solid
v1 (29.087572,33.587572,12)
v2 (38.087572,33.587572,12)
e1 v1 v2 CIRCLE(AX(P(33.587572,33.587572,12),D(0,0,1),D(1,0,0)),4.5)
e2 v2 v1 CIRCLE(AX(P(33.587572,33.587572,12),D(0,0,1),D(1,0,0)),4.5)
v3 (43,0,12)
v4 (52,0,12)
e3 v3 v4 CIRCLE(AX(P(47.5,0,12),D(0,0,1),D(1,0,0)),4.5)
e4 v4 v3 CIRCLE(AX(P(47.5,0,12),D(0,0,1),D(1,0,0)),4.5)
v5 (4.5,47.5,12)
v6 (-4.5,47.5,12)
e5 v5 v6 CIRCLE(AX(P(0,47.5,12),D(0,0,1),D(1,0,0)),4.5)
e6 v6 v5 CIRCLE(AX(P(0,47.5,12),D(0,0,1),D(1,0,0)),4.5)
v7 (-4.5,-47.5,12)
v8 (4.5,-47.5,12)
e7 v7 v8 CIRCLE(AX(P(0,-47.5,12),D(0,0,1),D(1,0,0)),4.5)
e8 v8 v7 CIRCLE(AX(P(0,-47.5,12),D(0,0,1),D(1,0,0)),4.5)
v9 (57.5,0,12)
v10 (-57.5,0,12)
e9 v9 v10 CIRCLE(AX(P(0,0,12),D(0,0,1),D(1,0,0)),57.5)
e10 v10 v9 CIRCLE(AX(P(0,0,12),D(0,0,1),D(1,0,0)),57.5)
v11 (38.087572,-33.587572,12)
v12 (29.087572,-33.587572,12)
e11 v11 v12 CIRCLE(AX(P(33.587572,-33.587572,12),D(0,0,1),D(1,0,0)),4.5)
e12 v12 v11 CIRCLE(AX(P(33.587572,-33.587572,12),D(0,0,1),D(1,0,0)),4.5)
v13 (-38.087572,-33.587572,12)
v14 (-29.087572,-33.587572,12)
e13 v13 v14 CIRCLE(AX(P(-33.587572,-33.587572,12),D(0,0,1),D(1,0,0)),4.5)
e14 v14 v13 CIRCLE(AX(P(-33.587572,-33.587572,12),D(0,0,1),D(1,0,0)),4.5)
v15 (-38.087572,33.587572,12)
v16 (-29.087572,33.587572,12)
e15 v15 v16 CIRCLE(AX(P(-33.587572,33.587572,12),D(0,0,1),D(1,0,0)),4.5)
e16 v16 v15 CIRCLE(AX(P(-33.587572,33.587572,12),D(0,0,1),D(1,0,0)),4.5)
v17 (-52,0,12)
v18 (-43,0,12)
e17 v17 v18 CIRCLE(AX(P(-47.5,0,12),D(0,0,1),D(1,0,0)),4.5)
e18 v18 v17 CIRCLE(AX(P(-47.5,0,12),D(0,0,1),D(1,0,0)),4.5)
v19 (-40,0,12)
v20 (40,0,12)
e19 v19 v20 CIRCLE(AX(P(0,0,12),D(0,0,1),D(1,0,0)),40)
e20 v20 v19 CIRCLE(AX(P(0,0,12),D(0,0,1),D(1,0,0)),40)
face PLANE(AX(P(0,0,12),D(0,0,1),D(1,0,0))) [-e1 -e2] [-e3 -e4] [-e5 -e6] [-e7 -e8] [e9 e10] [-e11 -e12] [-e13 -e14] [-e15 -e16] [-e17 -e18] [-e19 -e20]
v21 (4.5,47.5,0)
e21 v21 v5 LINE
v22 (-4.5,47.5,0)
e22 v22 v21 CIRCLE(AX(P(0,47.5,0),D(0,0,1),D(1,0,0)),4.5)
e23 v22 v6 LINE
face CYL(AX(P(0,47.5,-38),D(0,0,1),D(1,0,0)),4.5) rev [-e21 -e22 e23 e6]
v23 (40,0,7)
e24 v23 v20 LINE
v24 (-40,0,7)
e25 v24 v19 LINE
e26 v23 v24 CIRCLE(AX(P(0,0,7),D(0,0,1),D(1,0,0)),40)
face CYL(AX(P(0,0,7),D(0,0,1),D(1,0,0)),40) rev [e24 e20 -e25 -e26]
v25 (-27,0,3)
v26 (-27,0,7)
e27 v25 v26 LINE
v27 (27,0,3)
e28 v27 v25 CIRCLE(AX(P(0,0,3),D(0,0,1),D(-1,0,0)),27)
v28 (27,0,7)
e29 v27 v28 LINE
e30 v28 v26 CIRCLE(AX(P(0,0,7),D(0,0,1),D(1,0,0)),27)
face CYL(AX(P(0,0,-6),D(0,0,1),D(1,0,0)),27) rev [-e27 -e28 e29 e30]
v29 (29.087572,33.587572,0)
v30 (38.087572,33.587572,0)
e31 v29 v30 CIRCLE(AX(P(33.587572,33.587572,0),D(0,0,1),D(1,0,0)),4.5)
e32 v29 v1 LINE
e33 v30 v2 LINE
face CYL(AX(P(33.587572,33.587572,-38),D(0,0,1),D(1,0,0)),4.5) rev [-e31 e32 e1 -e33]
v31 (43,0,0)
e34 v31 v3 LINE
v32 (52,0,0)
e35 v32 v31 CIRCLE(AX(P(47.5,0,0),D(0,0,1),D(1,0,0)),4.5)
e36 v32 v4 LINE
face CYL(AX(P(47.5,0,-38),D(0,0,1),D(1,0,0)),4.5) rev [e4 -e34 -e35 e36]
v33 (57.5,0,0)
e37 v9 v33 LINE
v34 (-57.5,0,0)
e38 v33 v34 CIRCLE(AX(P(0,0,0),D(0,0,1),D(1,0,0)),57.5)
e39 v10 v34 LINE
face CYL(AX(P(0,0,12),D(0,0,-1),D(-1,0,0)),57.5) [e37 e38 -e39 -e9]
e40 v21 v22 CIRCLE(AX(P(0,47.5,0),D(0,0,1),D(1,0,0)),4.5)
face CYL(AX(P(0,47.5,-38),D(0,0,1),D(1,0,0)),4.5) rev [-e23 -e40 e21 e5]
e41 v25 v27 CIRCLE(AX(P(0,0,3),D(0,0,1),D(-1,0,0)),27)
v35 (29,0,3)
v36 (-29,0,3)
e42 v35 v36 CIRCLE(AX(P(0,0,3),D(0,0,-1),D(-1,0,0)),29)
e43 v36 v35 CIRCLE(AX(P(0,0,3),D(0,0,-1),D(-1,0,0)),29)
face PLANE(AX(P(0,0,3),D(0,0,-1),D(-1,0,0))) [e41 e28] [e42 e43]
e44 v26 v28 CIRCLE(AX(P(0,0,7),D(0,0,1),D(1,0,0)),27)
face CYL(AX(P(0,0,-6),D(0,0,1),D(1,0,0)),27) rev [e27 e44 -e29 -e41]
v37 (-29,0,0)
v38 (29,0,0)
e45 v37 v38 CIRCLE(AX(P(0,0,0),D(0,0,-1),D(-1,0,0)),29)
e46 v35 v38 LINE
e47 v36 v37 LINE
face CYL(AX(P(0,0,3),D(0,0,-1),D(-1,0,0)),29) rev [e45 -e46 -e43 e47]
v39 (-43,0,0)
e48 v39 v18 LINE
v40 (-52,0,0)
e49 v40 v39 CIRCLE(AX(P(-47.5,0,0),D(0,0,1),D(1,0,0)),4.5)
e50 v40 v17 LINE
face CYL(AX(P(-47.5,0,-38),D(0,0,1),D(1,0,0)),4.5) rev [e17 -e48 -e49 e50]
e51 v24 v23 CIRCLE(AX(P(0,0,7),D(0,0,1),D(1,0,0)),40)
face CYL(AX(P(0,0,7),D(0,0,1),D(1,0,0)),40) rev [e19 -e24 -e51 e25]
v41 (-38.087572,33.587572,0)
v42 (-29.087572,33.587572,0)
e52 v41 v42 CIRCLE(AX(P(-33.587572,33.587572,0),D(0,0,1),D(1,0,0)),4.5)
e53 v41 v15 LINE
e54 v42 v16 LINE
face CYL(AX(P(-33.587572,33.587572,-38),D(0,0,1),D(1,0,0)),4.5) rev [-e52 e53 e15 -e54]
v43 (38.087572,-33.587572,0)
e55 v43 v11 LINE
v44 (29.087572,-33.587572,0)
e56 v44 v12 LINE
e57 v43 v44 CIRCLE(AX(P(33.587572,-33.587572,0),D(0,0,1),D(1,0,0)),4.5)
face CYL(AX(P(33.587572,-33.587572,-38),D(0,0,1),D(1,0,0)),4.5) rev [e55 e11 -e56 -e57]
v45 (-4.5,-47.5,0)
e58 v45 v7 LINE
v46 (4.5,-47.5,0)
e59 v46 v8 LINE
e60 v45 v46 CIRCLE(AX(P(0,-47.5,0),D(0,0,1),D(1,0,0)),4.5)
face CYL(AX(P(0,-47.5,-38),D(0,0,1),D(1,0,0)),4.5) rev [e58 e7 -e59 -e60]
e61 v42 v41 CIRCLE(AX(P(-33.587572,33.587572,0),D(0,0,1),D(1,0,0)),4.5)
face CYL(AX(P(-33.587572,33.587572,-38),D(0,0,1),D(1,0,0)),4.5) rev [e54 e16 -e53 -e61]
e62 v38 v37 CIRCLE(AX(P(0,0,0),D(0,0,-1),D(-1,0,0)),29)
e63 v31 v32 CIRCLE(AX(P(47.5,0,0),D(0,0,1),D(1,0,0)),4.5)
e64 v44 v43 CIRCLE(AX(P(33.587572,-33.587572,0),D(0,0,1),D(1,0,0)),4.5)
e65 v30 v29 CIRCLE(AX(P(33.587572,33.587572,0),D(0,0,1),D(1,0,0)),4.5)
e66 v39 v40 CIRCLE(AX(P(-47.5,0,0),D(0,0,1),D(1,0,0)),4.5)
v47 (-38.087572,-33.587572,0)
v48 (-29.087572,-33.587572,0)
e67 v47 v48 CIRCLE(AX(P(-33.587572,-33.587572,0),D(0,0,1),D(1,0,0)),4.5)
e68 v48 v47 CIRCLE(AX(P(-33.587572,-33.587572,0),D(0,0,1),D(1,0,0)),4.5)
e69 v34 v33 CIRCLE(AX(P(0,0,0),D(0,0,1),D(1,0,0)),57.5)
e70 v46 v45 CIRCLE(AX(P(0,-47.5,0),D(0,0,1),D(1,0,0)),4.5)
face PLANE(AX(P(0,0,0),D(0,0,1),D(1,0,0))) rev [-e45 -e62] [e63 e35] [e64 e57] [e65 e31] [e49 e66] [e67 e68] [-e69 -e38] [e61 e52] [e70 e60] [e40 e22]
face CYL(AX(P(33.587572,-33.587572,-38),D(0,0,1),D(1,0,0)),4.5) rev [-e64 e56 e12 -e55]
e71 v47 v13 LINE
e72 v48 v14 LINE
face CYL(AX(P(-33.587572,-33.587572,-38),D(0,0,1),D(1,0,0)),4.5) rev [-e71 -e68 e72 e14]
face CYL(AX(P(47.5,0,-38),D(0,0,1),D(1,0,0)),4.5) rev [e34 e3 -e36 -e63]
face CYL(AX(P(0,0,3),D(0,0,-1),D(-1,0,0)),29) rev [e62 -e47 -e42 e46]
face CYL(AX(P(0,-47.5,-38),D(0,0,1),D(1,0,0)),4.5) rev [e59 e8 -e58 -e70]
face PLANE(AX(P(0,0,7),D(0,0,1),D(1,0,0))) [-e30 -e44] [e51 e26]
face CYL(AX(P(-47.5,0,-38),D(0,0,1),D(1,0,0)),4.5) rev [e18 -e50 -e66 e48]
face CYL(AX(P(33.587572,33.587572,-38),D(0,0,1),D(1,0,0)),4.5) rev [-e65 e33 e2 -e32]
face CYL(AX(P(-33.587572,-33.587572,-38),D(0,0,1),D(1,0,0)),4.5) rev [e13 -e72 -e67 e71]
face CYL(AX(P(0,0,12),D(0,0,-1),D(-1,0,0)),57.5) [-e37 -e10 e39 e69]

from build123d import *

# Parameters (mm, degrees)
SKETCH_1_R          = 57.5
EXTRUDE_1_DEPTH     = 12
SKETCH_2_R          = 40
CUT_EXTRUDE_1_DEPTH = 5
SKETCH_3_R          = 27
CUT_EXTRUDE_2_DEPTH = 13
SKETCH_4_R          = 29
CUT_EXTRUDE_3_DEPTH = 3
SKETCH_5_R          = 4.5
CUT_EXTRUDE_4_DEPTH = 50


with BuildPart() as part:
    # 草图1 → 凸台-拉伸1 (new body)
    with BuildSketch(Plane.XY):
        Circle(SKETCH_1_R)
    extrude(amount=EXTRUDE_1_DEPTH)

    # 草图2 → 切除-拉伸1 (cut)
    with BuildSketch(Plane.XY.offset(12)):
        Circle(SKETCH_2_R)
    extrude(amount=-CUT_EXTRUDE_1_DEPTH, mode=Mode.SUBTRACT)

    # 草图3 → 切除-拉伸2 (cut)
    with BuildSketch(Plane.XY.offset(7)):
        Circle(SKETCH_3_R)
    extrude(amount=-CUT_EXTRUDE_2_DEPTH, mode=Mode.SUBTRACT)

    # 草图4 → 切除-拉伸3 (cut)
    with BuildSketch(Plane(origin=(0, 0, 0), x_dir=(-1, 0, 0), z_dir=(0, 0, -1))):
        Circle(SKETCH_4_R)
    extrude(amount=-CUT_EXTRUDE_3_DEPTH, mode=Mode.SUBTRACT)

    # 草图5 → 切除-拉伸4 (cut)
    with BuildSketch(Plane.XY.offset(12)):
        with Locations((0, 47.5)):
            Circle(SKETCH_5_R)
        with Locations((33.587572106, 33.587572106)):
            Circle(SKETCH_5_R)
        with Locations((47.5, 0)):
            Circle(SKETCH_5_R)
        with Locations((33.587572106, -33.587572106)):
            Circle(SKETCH_5_R)
        with Locations((0, -47.5)):
            Circle(SKETCH_5_R)
        with Locations((-33.587572106, -33.587572106)):
            Circle(SKETCH_5_R)
        with Locations((-47.5, 0)):
            Circle(SKETCH_5_R)
        with Locations((-33.587572106, 33.587572106)):
            Circle(SKETCH_5_R)
    extrude(amount=-CUT_EXTRUDE_4_DEPTH, mode=Mode.SUBTRACT)


solid = part.part
